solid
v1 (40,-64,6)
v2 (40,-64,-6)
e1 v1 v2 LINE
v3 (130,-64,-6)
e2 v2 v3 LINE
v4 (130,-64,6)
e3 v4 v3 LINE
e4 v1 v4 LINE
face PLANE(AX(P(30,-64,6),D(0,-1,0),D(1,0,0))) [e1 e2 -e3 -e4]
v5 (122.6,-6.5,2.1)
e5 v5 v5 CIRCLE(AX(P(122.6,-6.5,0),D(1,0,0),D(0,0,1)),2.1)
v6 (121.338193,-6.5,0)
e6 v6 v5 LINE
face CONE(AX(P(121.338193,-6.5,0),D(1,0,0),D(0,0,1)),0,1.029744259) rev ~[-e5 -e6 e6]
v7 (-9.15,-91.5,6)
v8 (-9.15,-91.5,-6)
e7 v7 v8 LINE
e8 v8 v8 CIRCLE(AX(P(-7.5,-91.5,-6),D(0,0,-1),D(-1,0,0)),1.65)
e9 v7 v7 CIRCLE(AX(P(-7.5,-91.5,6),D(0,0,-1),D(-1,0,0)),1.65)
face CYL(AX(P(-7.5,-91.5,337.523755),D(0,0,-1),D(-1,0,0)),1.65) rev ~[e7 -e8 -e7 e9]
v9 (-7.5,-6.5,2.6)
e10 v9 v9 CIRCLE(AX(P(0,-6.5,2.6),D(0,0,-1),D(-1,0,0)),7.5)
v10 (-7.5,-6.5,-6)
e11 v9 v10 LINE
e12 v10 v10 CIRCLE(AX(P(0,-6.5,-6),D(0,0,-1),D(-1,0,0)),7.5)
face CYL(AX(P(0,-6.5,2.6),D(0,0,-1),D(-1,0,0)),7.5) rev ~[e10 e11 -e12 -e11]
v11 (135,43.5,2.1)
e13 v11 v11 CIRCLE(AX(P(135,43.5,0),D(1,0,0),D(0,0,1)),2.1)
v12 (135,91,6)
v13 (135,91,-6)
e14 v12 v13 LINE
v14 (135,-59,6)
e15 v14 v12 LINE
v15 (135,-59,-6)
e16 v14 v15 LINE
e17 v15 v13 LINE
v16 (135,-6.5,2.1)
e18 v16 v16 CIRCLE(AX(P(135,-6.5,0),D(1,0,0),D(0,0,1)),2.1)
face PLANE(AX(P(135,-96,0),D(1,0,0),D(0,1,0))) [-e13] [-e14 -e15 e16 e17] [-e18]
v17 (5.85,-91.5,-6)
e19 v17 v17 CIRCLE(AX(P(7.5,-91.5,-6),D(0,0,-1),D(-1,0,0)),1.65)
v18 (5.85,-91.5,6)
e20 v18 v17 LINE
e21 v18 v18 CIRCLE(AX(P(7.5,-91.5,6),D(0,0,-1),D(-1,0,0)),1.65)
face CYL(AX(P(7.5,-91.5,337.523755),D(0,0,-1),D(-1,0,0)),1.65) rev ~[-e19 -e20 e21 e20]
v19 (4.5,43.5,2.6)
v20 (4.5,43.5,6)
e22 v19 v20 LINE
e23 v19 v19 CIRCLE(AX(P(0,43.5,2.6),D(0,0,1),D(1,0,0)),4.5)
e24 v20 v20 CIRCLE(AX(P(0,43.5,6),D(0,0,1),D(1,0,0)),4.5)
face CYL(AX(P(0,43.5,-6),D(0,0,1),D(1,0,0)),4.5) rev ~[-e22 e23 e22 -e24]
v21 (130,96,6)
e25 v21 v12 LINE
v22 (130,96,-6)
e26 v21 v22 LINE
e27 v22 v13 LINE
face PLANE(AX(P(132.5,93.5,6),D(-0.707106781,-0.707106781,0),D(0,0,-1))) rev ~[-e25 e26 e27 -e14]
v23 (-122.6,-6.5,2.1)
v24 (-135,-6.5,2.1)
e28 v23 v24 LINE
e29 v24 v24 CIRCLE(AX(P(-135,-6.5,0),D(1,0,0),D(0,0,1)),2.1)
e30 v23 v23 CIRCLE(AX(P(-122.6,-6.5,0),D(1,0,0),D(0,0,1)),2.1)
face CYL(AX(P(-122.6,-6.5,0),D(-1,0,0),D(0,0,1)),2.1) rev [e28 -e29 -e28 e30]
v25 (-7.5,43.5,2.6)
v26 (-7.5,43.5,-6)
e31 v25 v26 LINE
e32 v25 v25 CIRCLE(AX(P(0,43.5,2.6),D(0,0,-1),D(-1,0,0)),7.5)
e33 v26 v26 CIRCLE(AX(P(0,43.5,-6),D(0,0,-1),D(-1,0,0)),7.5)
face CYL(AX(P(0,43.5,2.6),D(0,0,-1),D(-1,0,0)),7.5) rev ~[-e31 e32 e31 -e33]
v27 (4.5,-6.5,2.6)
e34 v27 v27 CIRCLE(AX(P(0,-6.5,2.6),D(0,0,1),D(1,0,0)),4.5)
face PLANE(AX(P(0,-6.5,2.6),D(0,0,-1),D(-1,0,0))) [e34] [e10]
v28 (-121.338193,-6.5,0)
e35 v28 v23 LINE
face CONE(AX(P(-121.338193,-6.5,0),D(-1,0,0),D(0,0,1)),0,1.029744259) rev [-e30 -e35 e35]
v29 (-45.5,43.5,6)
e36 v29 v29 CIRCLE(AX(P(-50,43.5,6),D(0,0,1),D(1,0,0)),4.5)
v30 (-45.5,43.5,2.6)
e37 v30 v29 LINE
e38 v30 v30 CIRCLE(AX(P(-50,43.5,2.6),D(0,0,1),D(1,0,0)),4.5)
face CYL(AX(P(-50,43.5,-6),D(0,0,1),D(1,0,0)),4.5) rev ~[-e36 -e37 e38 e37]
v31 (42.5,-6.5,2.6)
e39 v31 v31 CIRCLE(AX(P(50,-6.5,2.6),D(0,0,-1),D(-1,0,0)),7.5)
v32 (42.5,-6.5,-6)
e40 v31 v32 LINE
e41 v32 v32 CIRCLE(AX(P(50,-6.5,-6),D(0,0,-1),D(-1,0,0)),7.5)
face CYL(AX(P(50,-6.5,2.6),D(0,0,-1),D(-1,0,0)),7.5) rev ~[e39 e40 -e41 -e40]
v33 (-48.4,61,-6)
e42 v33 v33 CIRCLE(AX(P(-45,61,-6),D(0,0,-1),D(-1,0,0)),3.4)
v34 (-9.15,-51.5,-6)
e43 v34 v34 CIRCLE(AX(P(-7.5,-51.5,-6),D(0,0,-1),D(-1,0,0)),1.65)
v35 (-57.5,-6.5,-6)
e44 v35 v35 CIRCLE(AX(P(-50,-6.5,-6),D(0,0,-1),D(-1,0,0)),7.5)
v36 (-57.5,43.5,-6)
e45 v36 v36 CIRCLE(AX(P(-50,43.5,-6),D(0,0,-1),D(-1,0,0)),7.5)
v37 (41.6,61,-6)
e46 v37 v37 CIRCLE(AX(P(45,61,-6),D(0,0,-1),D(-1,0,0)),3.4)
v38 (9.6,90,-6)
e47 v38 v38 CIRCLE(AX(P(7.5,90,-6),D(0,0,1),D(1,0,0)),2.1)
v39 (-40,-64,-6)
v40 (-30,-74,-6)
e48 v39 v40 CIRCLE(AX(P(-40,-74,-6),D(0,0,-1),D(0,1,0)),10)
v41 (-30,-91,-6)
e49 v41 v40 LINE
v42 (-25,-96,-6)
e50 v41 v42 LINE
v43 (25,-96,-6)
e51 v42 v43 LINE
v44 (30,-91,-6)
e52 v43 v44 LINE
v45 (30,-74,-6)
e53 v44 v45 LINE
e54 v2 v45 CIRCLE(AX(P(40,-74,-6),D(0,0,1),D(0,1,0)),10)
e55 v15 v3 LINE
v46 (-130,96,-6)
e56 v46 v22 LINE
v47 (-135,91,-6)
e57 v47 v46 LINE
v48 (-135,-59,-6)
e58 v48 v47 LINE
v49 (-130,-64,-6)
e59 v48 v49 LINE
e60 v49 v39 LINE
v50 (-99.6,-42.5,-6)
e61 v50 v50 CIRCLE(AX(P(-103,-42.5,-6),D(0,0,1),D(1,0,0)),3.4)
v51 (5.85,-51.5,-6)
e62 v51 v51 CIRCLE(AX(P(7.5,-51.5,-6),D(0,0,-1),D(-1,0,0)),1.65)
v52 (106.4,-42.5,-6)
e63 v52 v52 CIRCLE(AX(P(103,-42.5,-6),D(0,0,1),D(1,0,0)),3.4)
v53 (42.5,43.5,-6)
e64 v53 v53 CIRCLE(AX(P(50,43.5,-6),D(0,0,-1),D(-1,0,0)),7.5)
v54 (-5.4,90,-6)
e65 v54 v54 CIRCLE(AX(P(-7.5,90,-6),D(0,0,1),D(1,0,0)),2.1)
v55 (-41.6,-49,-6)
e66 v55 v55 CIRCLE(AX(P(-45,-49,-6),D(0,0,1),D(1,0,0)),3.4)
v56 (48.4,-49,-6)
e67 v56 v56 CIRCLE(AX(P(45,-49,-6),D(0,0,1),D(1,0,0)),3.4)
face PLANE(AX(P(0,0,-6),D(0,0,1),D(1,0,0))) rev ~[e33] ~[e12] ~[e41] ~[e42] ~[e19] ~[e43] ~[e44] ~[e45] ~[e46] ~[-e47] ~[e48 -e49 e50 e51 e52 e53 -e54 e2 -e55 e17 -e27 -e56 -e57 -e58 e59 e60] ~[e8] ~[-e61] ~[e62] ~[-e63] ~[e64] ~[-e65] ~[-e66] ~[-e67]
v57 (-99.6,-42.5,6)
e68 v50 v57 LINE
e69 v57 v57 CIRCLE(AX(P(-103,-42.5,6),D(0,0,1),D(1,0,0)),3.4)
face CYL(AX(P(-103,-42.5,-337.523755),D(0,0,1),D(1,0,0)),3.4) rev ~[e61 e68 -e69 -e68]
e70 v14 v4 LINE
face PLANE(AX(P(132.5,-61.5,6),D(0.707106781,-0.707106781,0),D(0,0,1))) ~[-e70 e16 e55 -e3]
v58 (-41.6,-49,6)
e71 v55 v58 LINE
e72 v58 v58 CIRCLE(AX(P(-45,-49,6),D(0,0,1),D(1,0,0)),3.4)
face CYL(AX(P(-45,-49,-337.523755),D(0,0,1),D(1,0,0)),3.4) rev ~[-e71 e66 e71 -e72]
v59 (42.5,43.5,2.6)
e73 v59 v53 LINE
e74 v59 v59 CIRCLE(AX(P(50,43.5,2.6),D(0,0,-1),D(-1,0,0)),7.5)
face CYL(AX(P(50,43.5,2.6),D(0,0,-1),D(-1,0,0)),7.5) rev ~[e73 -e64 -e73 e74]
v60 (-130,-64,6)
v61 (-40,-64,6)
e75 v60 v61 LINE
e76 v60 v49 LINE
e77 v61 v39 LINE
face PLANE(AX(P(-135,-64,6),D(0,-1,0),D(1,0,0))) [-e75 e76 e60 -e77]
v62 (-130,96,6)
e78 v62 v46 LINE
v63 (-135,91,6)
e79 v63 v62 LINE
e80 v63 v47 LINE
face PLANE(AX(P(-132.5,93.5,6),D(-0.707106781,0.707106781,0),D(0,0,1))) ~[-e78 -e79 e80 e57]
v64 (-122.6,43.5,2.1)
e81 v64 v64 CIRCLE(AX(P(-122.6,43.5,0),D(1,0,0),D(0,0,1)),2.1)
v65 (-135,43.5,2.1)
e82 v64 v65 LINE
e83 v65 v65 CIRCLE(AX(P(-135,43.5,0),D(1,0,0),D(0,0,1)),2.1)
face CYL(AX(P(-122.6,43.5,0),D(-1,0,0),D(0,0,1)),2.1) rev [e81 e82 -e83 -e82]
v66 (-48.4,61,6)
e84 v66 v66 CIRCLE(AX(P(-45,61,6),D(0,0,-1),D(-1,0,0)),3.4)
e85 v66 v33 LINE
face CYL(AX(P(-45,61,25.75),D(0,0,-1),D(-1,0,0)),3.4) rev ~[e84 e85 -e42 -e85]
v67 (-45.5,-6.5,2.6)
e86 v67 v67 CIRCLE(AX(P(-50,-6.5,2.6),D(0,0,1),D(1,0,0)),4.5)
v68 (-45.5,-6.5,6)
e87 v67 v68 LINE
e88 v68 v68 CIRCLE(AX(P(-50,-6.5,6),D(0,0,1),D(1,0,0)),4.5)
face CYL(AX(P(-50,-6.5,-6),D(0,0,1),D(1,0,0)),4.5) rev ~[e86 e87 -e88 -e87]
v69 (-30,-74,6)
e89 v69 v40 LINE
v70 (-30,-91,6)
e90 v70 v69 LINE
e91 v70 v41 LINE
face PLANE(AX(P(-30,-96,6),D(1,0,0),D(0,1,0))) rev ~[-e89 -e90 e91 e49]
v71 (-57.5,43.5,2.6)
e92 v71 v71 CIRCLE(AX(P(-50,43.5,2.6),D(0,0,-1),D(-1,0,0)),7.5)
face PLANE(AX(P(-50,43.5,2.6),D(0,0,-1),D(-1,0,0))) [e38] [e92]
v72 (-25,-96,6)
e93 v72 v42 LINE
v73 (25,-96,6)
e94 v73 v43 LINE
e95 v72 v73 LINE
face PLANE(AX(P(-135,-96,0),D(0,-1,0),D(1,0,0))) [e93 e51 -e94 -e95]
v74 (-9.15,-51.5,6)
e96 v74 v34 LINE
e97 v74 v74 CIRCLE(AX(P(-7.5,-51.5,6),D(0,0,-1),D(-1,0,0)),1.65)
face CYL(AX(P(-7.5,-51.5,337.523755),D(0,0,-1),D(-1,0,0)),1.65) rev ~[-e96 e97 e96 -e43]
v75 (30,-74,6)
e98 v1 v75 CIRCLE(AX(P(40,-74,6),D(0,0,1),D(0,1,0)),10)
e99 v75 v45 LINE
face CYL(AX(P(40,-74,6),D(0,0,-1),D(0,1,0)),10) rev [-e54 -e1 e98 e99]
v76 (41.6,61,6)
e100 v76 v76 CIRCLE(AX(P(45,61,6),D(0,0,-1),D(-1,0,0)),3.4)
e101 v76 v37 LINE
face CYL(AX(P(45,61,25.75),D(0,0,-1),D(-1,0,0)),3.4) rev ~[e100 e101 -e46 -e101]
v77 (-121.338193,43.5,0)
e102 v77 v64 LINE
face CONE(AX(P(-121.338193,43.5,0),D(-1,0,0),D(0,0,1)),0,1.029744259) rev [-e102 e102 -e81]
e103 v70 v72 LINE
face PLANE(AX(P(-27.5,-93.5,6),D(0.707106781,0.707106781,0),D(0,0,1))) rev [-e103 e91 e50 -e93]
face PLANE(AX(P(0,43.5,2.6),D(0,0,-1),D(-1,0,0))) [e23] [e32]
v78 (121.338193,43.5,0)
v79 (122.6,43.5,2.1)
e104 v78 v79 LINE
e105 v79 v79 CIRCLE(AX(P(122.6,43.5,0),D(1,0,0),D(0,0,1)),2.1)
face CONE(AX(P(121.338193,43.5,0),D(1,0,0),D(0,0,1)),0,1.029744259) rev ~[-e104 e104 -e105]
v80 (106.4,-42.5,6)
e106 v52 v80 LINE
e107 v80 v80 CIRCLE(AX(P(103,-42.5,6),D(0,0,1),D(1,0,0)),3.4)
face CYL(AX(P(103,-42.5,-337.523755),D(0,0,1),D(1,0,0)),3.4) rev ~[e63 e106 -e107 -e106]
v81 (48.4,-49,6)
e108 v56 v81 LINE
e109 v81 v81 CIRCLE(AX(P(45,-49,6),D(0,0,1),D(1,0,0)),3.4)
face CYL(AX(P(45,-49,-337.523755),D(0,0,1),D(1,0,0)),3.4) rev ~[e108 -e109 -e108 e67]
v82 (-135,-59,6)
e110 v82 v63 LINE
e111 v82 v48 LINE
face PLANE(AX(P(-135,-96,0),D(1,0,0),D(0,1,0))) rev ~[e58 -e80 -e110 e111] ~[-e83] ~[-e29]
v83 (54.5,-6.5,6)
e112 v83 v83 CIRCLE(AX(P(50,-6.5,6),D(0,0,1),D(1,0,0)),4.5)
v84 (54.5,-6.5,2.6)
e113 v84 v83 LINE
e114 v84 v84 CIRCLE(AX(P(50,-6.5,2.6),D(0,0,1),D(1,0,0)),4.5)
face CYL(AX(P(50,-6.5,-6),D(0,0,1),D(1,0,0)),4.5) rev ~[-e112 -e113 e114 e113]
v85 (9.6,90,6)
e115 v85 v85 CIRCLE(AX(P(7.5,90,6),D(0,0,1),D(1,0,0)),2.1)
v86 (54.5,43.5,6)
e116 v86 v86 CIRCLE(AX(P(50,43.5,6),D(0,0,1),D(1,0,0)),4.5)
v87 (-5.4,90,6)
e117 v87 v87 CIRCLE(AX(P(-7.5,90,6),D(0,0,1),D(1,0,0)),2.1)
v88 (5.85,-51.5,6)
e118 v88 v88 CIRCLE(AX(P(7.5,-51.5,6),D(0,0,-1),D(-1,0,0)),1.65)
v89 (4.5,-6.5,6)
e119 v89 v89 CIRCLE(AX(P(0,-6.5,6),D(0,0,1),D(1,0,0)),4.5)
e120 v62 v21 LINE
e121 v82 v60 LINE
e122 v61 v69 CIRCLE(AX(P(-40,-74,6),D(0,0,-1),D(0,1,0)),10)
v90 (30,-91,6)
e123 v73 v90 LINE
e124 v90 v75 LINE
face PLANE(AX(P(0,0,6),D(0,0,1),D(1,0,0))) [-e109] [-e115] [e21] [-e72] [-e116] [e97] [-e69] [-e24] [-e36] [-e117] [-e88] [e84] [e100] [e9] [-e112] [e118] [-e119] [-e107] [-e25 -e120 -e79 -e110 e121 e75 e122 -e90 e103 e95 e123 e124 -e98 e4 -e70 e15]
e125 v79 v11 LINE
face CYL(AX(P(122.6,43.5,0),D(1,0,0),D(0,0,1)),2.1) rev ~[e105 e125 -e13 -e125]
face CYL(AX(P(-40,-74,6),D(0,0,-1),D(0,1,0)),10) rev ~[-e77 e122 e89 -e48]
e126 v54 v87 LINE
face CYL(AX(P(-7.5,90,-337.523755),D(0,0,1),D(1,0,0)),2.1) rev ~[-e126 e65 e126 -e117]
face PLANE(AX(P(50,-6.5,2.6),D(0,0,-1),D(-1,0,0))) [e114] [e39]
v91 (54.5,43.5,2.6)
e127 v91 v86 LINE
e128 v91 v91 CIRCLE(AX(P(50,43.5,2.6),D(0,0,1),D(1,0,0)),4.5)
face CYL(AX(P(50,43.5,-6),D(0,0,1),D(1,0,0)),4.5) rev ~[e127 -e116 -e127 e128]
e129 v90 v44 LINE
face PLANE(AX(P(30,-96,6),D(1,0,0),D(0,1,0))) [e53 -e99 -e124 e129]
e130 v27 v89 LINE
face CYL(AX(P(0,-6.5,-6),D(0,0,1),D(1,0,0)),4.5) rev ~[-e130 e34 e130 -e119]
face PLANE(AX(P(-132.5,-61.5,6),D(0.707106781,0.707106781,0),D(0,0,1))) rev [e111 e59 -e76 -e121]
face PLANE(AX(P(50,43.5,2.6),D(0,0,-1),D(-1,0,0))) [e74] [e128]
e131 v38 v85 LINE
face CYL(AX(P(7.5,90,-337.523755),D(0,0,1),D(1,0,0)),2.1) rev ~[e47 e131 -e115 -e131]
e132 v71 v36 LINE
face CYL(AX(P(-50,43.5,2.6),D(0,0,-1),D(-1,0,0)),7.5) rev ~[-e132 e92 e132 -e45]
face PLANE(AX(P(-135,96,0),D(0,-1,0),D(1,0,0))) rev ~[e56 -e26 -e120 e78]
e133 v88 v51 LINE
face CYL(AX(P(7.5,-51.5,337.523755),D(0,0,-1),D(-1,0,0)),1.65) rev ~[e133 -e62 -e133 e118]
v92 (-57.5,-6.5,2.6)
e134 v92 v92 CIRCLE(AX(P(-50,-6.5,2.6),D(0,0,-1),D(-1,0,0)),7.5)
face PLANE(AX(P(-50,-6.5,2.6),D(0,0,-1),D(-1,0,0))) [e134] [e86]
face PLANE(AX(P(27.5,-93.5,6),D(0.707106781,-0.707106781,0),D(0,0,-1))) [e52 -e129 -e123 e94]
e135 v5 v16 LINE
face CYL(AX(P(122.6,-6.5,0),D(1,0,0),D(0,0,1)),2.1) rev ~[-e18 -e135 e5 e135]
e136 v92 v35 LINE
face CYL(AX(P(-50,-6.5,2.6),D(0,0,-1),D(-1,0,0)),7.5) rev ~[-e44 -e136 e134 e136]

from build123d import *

# Parameters (mm, degrees)
SKETCH_1_W                   = 270
SKETCH_1_H                   = 192
EXTRUDE_1_DEPTH              = 6
SKETCH_2_W                   = 105
SKETCH_2_H                   = 32
CUT_EXTRUDE_1_DEPTH          = 12
HOLE_WIZARD_M8_1_D           = 6.8
HOLE_WIZARD_M8_1_DEPTH       = 19.75
HOLE_WIZARD_M8_1_TIP         = 2.042926105
HOLE_WIZARD_M4_1_D           = 3.3
CHAMFER_1_SIZE               = 5
FILLET_1_R                   = 10
HOLE_WIZARD_M8_2_D           = 6.8
HOLE_WIZARD_M8_3_D           = 9
HOLE_WIZARD_M8_3_DEPTH       = 24.5
HOLE_WIZARD_M8_3_CBORE_D     = 15
HOLE_WIZARD_M8_3_CBORE_DEPTH = 8.6
HOLE_WIZARD_M8_3_TIP         = 2.703872786
HOLE_WIZARD_M5_2_D           = 4.2
HOLE_WIZARD_M5_3_AT_2_COUNT  = 2
HOLE_WIZARD_M5_3_AT_2_PITCH  = 50


with BuildPart() as part:
    # 草图1 → 凸台-拉伸1 (new, symmetric)
    with BuildSketch(Plane.XY):
        Rectangle(SKETCH_1_W, SKETCH_1_H)
    extrude(amount=EXTRUDE_1_DEPTH, both=True)

    # 草图2 → 切除-拉伸1 (cut)
    with BuildSketch(Plane.XY.offset(6)):
        with Locations((-82.5, -80)):
            Rectangle(SKETCH_2_W, SKETCH_2_H)
        with Locations((82.5, -80)):
            Rectangle(SKETCH_2_W, SKETCH_2_H)
    extrude(amount=-CUT_EXTRUDE_1_DEPTH, mode=Mode.SUBTRACT)

    # M8 螺纹孔1
    with Locations(Plane.XY.offset(6)):
        with Locations((-45, 61), (45, 61)):
            Hole(HOLE_WIZARD_M8_1_D / 2, depth=HOLE_WIZARD_M8_1_DEPTH)
            with Locations((0, 0, -(HOLE_WIZARD_M8_1_DEPTH + HOLE_WIZARD_M8_1_TIP / 2))):  # 118° drill point
                Cone(0, HOLE_WIZARD_M8_1_D / 2, HOLE_WIZARD_M8_1_TIP, mode=Mode.SUBTRACT)

    # M4 螺纹孔1 (through all)
    with Locations(Plane.XY.offset(6)):
        with Locations((-7.5, -91.5), (7.5, -91.5), (-7.5, -51.5), (7.5, -51.5)):
            Hole(HOLE_WIZARD_M4_1_D / 2)

    # 倒角1
    chamfer_1_edges = [part.edges().sort_by_distance(p)[0] for p in [
        (-135, -64, 0),
        (-30, -96, 0),
        (30, -96, 0),
        (135, -64, 0),
        (-135, 96, 0),
        (135, 96, 0),
    ]]
    chamfer(chamfer_1_edges, length=CHAMFER_1_SIZE)

    # 圆角1
    fillet_1_edges = [part.edges().sort_by_distance(p)[0] for p in [
        (-30, -64, 0),
        (30, -64, 0),
    ]]
    fillet(fillet_1_edges, radius=FILLET_1_R)

    # Hole Wizard M8 _2 (through all)
    with Locations(Plane(origin=(0, 0, -6), x_dir=(-1, 0, 0), z_dir=(0, 0, -1))):
        with Locations((-45, -49), (45, -49), (-103, -42.5), (103, -42.5)):
            Hole(HOLE_WIZARD_M8_2_D / 2)

    # M8 六角凹头螺钉的柱形沉头孔3
    with Locations(Plane(origin=(0, 0, -6), x_dir=(-1, 0, 0), z_dir=(0, 0, -1))):
        with Locations((-50, 43.5), (-50, -6.5), (0, 43.5), (0, -6.5), (50, 43.5), (50, -6.5)):
            CounterBoreHole(HOLE_WIZARD_M8_3_D / 2, HOLE_WIZARD_M8_3_CBORE_D / 2, HOLE_WIZARD_M8_3_CBORE_DEPTH, depth=HOLE_WIZARD_M8_3_DEPTH)
            with Locations((0, 0, -(HOLE_WIZARD_M8_3_DEPTH + HOLE_WIZARD_M8_3_TIP / 2))):  # 118° drill point
                Cone(0, HOLE_WIZARD_M8_3_D / 2, HOLE_WIZARD_M8_3_TIP, mode=Mode.SUBTRACT)

    # M5 螺纹孔2 (through all)
    with Locations(Plane(origin=(0, 0, -6), x_dir=(-1, 0, 0), z_dir=(0, 0, -1))):
        with Locations((-7.5, 90), (7.5, 90)):
            Hole(HOLE_WIZARD_M5_2_D / 2)

    # 草图23 → M5 螺纹孔3 (revolve, cut)
    with BuildSketch(Plane(origin=(-135, -6.5, 0), x_dir=(0, 0, 1), z_dir=(0, 1, 0))):
        Polygon((0, 0), (0, 13.6618073), (2.1, 12.4), (2.1, 0), align=None)
    hole_wizard_m5_3 = revolve(axis=Axis((-141.35, -6.5, 0), (1, 0, 0)), mode=Mode.SUBTRACT)

    # M5 螺纹孔3 at 2: M5 螺纹孔3 ×2
    with Locations(*[(0, i * HOLE_WIZARD_M5_3_AT_2_PITCH, 0) for i in range(1, HOLE_WIZARD_M5_3_AT_2_COUNT)]):
        add(hole_wizard_m5_3, mode=Mode.SUBTRACT)

    # 镜向1: M5 螺纹孔3 across plane
    add(hole_wizard_m5_3.mirror(Plane(origin=(0, 0, 0), x_dir=(0, 0, 1), z_dir=(1, 0, 0))), mode=Mode.SUBTRACT)

    # 镜向1 copy 1 sketch → 镜向1 copy 1 (revolve, cut)
    with BuildSketch(Plane(origin=(135, 43.5, 0), x_dir=(0, 0, 1), z_dir=(0, 1, 0))):
        Polygon((0, 0), (0, -13.6618073), (2.1, -12.4), (2.1, 0), align=None)
    revolve(axis=Axis((141.35, 43.5, 0), (1, 0, 0)), mode=Mode.SUBTRACT)


solid = part.part
